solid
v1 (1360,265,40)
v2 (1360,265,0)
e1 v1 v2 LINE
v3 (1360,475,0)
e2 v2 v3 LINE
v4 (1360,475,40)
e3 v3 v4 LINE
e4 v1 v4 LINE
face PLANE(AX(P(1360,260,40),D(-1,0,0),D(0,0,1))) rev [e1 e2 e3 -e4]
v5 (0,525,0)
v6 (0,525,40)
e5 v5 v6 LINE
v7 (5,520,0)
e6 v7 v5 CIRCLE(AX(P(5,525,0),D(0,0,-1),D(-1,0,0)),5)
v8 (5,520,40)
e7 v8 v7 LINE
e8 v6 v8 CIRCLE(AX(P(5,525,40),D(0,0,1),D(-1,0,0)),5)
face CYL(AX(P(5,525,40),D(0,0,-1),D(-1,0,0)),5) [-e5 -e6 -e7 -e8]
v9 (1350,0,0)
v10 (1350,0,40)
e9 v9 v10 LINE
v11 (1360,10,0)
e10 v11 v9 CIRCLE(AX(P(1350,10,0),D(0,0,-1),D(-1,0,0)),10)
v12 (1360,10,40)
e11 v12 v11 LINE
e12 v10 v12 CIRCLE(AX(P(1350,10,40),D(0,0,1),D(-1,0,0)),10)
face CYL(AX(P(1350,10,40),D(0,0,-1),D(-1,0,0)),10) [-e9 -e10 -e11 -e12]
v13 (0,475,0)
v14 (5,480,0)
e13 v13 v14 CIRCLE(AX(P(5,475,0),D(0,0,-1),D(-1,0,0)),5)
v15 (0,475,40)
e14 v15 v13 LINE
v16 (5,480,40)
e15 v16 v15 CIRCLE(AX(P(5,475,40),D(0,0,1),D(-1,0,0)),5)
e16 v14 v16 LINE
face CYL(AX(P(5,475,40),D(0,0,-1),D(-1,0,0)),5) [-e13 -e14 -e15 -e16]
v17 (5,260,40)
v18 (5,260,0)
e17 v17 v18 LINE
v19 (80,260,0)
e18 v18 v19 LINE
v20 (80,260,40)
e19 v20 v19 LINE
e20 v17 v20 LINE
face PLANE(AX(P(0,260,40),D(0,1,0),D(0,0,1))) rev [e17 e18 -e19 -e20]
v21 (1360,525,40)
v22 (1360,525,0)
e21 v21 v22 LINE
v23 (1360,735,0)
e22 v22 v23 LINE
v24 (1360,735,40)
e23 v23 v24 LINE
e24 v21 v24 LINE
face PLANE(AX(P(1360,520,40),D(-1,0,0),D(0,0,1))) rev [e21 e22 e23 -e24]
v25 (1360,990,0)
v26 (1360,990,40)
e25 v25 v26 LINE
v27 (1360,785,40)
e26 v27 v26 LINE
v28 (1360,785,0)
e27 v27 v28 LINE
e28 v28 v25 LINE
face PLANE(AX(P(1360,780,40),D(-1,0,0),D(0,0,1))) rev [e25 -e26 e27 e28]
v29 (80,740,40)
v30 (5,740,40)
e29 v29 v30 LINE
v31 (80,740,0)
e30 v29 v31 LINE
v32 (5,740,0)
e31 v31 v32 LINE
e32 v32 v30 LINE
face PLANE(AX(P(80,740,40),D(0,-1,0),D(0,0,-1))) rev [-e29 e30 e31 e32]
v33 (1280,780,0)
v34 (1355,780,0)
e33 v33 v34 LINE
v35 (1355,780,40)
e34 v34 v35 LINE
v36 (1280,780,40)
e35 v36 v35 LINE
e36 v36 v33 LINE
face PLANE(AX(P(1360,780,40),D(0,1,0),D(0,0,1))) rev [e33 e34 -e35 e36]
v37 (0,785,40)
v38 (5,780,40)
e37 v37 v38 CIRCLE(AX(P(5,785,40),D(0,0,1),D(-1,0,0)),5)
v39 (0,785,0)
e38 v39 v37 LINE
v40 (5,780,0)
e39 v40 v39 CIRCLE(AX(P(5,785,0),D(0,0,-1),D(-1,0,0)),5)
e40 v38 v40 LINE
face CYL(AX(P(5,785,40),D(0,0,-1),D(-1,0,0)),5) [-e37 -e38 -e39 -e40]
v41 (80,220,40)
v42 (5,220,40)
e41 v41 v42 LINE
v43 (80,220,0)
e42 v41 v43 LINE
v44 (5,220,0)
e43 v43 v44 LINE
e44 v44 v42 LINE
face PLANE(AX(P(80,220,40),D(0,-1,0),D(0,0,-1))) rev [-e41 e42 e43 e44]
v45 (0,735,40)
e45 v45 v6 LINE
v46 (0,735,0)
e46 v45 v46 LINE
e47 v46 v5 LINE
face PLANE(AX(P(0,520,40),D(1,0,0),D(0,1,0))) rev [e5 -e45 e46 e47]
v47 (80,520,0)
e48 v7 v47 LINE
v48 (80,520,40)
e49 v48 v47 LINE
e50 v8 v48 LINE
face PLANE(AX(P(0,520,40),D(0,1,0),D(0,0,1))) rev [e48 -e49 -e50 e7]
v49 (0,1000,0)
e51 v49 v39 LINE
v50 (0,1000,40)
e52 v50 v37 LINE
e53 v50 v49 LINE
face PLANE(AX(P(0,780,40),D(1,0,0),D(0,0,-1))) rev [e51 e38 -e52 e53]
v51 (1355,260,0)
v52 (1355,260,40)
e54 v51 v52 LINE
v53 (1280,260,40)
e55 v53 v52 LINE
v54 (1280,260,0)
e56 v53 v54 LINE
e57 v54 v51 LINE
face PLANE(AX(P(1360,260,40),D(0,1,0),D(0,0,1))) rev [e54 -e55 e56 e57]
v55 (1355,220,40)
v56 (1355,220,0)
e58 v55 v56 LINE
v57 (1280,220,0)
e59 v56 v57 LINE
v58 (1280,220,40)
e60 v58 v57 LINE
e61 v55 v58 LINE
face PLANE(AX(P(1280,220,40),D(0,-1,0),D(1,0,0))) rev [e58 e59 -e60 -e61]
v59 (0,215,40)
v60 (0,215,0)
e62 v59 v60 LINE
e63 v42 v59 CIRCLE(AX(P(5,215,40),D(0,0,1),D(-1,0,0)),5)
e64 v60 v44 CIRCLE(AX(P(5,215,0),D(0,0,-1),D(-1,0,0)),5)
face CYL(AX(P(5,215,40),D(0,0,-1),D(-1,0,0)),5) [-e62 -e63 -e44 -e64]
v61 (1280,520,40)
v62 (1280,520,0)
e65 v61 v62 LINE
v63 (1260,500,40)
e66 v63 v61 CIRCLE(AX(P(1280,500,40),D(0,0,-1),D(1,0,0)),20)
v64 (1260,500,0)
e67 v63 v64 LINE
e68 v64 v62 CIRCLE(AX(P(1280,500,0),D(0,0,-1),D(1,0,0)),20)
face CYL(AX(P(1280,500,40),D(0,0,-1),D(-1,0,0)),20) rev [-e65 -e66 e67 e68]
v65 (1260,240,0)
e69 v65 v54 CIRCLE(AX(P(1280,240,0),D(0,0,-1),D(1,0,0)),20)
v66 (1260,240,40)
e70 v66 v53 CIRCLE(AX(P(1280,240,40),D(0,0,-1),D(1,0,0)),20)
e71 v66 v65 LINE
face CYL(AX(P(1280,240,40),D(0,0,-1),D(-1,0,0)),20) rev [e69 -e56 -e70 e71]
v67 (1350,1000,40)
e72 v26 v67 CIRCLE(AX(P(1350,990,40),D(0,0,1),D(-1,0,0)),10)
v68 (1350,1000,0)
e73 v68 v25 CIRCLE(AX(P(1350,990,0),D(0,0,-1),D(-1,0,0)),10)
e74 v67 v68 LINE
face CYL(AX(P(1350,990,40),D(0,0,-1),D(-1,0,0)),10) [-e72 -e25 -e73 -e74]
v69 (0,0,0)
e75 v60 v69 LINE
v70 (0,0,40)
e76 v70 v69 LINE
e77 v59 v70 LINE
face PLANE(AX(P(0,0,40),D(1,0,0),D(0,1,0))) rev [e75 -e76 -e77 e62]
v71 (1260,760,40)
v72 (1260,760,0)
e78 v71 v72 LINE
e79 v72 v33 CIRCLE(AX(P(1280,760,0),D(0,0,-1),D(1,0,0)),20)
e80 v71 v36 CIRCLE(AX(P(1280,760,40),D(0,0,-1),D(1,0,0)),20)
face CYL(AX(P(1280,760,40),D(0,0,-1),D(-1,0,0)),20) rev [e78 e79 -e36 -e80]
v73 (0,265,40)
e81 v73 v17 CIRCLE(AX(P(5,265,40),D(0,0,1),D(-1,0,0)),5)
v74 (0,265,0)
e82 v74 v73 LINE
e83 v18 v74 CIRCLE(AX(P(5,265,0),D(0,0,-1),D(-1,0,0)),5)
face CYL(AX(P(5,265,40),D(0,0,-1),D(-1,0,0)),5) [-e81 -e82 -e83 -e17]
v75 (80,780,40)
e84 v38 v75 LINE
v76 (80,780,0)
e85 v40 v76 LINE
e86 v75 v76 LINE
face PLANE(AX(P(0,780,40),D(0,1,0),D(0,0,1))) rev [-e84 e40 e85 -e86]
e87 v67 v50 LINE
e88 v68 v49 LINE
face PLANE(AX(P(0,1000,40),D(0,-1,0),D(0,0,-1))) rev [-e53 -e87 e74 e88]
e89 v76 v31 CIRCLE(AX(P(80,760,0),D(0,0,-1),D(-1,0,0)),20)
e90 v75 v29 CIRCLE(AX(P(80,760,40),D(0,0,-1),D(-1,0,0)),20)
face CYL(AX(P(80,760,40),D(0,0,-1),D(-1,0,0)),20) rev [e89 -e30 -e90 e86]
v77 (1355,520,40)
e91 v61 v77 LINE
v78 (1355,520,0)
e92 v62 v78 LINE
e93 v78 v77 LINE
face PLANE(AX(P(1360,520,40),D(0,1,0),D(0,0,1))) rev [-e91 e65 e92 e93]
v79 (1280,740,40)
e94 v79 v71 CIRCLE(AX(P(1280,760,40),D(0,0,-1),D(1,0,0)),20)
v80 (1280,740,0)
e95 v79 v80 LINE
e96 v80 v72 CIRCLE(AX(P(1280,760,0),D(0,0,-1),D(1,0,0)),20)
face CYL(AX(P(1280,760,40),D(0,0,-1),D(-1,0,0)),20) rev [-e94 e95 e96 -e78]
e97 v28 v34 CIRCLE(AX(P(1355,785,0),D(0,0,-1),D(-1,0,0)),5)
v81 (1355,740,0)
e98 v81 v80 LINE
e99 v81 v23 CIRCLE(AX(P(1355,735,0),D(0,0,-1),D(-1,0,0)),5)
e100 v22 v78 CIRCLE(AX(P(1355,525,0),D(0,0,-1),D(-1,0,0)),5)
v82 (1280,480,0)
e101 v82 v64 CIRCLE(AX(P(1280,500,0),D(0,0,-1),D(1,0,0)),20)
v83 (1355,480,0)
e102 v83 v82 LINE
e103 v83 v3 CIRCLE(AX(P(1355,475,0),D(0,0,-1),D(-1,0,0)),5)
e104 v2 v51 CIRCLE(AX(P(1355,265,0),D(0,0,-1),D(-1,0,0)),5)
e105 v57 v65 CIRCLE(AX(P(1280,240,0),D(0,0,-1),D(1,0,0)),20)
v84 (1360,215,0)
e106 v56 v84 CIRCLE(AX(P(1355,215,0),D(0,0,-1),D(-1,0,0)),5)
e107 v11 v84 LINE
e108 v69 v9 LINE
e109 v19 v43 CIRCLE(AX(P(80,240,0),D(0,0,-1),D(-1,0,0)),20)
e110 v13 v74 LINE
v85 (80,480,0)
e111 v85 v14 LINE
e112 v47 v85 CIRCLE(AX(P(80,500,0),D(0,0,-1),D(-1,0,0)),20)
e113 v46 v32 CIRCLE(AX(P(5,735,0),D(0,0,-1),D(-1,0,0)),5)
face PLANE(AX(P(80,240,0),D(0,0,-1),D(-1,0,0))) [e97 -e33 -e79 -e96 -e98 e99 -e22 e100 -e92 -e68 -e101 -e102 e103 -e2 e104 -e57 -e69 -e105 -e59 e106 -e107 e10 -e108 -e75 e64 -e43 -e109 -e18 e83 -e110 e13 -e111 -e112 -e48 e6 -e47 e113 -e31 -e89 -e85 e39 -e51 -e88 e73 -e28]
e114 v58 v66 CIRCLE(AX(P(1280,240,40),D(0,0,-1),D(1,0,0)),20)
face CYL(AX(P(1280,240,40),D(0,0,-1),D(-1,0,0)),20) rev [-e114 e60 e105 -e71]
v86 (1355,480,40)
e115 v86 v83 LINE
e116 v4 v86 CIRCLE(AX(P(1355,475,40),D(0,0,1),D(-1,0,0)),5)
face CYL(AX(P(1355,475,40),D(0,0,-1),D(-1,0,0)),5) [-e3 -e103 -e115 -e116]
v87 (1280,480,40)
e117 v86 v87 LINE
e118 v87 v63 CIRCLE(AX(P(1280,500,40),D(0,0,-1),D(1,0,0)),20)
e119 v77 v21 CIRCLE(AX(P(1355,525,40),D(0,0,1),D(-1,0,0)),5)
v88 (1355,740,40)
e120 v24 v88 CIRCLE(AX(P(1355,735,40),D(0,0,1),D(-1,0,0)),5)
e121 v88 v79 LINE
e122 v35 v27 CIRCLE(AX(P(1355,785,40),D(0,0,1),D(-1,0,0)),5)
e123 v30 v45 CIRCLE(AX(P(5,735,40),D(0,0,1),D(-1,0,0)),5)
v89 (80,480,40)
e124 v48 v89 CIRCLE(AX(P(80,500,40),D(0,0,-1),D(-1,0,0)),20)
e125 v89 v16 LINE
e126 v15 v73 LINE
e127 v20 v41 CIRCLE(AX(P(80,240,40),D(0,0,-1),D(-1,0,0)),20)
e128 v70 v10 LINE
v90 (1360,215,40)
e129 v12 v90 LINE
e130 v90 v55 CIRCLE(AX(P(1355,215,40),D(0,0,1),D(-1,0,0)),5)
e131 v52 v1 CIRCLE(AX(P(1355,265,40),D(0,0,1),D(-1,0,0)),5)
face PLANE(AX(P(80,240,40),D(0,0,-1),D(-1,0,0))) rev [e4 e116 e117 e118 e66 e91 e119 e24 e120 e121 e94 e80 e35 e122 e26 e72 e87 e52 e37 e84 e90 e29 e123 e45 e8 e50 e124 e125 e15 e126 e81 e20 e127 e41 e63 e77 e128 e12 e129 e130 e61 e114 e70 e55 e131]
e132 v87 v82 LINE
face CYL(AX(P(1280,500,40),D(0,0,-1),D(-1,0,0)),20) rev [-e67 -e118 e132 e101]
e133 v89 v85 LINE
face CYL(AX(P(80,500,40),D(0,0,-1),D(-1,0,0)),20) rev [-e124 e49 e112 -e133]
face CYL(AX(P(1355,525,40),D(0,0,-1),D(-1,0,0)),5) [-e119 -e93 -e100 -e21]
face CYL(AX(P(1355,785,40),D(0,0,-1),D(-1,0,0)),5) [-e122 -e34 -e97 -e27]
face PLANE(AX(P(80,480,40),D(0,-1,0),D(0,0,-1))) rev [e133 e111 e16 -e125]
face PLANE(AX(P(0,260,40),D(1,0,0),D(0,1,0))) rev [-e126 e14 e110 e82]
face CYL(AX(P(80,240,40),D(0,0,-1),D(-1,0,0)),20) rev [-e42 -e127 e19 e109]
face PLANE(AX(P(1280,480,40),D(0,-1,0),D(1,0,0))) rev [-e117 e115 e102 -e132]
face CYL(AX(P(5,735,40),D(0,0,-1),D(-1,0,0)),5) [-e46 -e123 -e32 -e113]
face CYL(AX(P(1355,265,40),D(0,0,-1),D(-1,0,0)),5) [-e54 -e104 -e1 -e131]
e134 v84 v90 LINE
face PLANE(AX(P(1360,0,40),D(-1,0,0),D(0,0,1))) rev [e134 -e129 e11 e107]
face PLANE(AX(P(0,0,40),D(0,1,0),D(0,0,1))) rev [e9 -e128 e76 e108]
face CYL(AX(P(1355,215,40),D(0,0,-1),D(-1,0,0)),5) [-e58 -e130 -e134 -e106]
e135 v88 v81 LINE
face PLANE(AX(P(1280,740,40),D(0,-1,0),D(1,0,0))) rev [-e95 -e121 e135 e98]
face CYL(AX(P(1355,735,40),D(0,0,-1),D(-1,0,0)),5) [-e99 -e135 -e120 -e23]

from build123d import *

# Parameters (mm, degrees)
BOSS_EXTRUDE1_DEPTH = 40
FILLET1_R           = 5
FILLET2_R           = 10


with BuildPart() as part:
    # Sketch1 → Boss-Extrude1 (new body)
    with BuildSketch(Plane.XY):
        with BuildLine():
            Line((0, 780), (80, 780))
            ThreePointArc((80, 780), (100, 760), (80, 740))
            Line((80, 740), (0, 740))
            Line((0, 740), (0, 520))
            Line((0, 520), (80, 520))
            ThreePointArc((80, 520), (100, 500), (80, 480))
            Line((80, 480), (0, 480))
            Line((0, 480), (0, 260))
            Line((0, 260), (80, 260))
            ThreePointArc((80, 260), (100, 240), (80, 220))
            Line((80, 220), (0, 220))
            Line((0, 220), (0, 0))
            Line((0, 0), (1360, 0))
            Line((1360, 0), (1360, 220))
            Line((1360, 220), (1280, 220))
            ThreePointArc((1280, 220), (1260, 240), (1280, 260))
            Line((1280, 260), (1360, 260))
            Line((1360, 260), (1360, 480))
            Line((1360, 480), (1280, 480))
            ThreePointArc((1280, 480), (1260, 500), (1280, 520))
            Line((1280, 520), (1360, 520))
            Line((1360, 520), (1360, 740))
            Line((1360, 740), (1280, 740))
            ThreePointArc((1280, 740), (1260, 760), (1280, 780))
            Line((1280, 780), (1360, 780))
            Line((1360, 780), (1360, 1000))
            Line((1360, 1000), (0, 1000))
            Line((0, 1000), (0, 780))
        make_face()
    extrude(amount=BOSS_EXTRUDE1_DEPTH)

    # Fillet1
    fillet1_edges = [part.edges().sort_by_distance(p)[0] for p in [
        (0, 220, 20),
        (0, 260, 20),
        (0, 480, 20),
        (0, 520, 20),
        (0, 740, 20),
        (0, 780, 20),
        (1360, 780, 20),
        (1360, 740, 20),
        (1360, 520, 20),
        (1360, 480, 20),
        (1360, 260, 20),
        (1360, 220, 20),
    ]]
    fillet(fillet1_edges, radius=FILLET1_R)

    # Fillet2
    fillet2_edges = [part.edges().sort_by_distance(p)[0] for p in [
        (1360, 1000, 20),
        (1360, 0, 20),
    ]]
    fillet(fillet2_edges, radius=FILLET2_R)


solid = part.part
